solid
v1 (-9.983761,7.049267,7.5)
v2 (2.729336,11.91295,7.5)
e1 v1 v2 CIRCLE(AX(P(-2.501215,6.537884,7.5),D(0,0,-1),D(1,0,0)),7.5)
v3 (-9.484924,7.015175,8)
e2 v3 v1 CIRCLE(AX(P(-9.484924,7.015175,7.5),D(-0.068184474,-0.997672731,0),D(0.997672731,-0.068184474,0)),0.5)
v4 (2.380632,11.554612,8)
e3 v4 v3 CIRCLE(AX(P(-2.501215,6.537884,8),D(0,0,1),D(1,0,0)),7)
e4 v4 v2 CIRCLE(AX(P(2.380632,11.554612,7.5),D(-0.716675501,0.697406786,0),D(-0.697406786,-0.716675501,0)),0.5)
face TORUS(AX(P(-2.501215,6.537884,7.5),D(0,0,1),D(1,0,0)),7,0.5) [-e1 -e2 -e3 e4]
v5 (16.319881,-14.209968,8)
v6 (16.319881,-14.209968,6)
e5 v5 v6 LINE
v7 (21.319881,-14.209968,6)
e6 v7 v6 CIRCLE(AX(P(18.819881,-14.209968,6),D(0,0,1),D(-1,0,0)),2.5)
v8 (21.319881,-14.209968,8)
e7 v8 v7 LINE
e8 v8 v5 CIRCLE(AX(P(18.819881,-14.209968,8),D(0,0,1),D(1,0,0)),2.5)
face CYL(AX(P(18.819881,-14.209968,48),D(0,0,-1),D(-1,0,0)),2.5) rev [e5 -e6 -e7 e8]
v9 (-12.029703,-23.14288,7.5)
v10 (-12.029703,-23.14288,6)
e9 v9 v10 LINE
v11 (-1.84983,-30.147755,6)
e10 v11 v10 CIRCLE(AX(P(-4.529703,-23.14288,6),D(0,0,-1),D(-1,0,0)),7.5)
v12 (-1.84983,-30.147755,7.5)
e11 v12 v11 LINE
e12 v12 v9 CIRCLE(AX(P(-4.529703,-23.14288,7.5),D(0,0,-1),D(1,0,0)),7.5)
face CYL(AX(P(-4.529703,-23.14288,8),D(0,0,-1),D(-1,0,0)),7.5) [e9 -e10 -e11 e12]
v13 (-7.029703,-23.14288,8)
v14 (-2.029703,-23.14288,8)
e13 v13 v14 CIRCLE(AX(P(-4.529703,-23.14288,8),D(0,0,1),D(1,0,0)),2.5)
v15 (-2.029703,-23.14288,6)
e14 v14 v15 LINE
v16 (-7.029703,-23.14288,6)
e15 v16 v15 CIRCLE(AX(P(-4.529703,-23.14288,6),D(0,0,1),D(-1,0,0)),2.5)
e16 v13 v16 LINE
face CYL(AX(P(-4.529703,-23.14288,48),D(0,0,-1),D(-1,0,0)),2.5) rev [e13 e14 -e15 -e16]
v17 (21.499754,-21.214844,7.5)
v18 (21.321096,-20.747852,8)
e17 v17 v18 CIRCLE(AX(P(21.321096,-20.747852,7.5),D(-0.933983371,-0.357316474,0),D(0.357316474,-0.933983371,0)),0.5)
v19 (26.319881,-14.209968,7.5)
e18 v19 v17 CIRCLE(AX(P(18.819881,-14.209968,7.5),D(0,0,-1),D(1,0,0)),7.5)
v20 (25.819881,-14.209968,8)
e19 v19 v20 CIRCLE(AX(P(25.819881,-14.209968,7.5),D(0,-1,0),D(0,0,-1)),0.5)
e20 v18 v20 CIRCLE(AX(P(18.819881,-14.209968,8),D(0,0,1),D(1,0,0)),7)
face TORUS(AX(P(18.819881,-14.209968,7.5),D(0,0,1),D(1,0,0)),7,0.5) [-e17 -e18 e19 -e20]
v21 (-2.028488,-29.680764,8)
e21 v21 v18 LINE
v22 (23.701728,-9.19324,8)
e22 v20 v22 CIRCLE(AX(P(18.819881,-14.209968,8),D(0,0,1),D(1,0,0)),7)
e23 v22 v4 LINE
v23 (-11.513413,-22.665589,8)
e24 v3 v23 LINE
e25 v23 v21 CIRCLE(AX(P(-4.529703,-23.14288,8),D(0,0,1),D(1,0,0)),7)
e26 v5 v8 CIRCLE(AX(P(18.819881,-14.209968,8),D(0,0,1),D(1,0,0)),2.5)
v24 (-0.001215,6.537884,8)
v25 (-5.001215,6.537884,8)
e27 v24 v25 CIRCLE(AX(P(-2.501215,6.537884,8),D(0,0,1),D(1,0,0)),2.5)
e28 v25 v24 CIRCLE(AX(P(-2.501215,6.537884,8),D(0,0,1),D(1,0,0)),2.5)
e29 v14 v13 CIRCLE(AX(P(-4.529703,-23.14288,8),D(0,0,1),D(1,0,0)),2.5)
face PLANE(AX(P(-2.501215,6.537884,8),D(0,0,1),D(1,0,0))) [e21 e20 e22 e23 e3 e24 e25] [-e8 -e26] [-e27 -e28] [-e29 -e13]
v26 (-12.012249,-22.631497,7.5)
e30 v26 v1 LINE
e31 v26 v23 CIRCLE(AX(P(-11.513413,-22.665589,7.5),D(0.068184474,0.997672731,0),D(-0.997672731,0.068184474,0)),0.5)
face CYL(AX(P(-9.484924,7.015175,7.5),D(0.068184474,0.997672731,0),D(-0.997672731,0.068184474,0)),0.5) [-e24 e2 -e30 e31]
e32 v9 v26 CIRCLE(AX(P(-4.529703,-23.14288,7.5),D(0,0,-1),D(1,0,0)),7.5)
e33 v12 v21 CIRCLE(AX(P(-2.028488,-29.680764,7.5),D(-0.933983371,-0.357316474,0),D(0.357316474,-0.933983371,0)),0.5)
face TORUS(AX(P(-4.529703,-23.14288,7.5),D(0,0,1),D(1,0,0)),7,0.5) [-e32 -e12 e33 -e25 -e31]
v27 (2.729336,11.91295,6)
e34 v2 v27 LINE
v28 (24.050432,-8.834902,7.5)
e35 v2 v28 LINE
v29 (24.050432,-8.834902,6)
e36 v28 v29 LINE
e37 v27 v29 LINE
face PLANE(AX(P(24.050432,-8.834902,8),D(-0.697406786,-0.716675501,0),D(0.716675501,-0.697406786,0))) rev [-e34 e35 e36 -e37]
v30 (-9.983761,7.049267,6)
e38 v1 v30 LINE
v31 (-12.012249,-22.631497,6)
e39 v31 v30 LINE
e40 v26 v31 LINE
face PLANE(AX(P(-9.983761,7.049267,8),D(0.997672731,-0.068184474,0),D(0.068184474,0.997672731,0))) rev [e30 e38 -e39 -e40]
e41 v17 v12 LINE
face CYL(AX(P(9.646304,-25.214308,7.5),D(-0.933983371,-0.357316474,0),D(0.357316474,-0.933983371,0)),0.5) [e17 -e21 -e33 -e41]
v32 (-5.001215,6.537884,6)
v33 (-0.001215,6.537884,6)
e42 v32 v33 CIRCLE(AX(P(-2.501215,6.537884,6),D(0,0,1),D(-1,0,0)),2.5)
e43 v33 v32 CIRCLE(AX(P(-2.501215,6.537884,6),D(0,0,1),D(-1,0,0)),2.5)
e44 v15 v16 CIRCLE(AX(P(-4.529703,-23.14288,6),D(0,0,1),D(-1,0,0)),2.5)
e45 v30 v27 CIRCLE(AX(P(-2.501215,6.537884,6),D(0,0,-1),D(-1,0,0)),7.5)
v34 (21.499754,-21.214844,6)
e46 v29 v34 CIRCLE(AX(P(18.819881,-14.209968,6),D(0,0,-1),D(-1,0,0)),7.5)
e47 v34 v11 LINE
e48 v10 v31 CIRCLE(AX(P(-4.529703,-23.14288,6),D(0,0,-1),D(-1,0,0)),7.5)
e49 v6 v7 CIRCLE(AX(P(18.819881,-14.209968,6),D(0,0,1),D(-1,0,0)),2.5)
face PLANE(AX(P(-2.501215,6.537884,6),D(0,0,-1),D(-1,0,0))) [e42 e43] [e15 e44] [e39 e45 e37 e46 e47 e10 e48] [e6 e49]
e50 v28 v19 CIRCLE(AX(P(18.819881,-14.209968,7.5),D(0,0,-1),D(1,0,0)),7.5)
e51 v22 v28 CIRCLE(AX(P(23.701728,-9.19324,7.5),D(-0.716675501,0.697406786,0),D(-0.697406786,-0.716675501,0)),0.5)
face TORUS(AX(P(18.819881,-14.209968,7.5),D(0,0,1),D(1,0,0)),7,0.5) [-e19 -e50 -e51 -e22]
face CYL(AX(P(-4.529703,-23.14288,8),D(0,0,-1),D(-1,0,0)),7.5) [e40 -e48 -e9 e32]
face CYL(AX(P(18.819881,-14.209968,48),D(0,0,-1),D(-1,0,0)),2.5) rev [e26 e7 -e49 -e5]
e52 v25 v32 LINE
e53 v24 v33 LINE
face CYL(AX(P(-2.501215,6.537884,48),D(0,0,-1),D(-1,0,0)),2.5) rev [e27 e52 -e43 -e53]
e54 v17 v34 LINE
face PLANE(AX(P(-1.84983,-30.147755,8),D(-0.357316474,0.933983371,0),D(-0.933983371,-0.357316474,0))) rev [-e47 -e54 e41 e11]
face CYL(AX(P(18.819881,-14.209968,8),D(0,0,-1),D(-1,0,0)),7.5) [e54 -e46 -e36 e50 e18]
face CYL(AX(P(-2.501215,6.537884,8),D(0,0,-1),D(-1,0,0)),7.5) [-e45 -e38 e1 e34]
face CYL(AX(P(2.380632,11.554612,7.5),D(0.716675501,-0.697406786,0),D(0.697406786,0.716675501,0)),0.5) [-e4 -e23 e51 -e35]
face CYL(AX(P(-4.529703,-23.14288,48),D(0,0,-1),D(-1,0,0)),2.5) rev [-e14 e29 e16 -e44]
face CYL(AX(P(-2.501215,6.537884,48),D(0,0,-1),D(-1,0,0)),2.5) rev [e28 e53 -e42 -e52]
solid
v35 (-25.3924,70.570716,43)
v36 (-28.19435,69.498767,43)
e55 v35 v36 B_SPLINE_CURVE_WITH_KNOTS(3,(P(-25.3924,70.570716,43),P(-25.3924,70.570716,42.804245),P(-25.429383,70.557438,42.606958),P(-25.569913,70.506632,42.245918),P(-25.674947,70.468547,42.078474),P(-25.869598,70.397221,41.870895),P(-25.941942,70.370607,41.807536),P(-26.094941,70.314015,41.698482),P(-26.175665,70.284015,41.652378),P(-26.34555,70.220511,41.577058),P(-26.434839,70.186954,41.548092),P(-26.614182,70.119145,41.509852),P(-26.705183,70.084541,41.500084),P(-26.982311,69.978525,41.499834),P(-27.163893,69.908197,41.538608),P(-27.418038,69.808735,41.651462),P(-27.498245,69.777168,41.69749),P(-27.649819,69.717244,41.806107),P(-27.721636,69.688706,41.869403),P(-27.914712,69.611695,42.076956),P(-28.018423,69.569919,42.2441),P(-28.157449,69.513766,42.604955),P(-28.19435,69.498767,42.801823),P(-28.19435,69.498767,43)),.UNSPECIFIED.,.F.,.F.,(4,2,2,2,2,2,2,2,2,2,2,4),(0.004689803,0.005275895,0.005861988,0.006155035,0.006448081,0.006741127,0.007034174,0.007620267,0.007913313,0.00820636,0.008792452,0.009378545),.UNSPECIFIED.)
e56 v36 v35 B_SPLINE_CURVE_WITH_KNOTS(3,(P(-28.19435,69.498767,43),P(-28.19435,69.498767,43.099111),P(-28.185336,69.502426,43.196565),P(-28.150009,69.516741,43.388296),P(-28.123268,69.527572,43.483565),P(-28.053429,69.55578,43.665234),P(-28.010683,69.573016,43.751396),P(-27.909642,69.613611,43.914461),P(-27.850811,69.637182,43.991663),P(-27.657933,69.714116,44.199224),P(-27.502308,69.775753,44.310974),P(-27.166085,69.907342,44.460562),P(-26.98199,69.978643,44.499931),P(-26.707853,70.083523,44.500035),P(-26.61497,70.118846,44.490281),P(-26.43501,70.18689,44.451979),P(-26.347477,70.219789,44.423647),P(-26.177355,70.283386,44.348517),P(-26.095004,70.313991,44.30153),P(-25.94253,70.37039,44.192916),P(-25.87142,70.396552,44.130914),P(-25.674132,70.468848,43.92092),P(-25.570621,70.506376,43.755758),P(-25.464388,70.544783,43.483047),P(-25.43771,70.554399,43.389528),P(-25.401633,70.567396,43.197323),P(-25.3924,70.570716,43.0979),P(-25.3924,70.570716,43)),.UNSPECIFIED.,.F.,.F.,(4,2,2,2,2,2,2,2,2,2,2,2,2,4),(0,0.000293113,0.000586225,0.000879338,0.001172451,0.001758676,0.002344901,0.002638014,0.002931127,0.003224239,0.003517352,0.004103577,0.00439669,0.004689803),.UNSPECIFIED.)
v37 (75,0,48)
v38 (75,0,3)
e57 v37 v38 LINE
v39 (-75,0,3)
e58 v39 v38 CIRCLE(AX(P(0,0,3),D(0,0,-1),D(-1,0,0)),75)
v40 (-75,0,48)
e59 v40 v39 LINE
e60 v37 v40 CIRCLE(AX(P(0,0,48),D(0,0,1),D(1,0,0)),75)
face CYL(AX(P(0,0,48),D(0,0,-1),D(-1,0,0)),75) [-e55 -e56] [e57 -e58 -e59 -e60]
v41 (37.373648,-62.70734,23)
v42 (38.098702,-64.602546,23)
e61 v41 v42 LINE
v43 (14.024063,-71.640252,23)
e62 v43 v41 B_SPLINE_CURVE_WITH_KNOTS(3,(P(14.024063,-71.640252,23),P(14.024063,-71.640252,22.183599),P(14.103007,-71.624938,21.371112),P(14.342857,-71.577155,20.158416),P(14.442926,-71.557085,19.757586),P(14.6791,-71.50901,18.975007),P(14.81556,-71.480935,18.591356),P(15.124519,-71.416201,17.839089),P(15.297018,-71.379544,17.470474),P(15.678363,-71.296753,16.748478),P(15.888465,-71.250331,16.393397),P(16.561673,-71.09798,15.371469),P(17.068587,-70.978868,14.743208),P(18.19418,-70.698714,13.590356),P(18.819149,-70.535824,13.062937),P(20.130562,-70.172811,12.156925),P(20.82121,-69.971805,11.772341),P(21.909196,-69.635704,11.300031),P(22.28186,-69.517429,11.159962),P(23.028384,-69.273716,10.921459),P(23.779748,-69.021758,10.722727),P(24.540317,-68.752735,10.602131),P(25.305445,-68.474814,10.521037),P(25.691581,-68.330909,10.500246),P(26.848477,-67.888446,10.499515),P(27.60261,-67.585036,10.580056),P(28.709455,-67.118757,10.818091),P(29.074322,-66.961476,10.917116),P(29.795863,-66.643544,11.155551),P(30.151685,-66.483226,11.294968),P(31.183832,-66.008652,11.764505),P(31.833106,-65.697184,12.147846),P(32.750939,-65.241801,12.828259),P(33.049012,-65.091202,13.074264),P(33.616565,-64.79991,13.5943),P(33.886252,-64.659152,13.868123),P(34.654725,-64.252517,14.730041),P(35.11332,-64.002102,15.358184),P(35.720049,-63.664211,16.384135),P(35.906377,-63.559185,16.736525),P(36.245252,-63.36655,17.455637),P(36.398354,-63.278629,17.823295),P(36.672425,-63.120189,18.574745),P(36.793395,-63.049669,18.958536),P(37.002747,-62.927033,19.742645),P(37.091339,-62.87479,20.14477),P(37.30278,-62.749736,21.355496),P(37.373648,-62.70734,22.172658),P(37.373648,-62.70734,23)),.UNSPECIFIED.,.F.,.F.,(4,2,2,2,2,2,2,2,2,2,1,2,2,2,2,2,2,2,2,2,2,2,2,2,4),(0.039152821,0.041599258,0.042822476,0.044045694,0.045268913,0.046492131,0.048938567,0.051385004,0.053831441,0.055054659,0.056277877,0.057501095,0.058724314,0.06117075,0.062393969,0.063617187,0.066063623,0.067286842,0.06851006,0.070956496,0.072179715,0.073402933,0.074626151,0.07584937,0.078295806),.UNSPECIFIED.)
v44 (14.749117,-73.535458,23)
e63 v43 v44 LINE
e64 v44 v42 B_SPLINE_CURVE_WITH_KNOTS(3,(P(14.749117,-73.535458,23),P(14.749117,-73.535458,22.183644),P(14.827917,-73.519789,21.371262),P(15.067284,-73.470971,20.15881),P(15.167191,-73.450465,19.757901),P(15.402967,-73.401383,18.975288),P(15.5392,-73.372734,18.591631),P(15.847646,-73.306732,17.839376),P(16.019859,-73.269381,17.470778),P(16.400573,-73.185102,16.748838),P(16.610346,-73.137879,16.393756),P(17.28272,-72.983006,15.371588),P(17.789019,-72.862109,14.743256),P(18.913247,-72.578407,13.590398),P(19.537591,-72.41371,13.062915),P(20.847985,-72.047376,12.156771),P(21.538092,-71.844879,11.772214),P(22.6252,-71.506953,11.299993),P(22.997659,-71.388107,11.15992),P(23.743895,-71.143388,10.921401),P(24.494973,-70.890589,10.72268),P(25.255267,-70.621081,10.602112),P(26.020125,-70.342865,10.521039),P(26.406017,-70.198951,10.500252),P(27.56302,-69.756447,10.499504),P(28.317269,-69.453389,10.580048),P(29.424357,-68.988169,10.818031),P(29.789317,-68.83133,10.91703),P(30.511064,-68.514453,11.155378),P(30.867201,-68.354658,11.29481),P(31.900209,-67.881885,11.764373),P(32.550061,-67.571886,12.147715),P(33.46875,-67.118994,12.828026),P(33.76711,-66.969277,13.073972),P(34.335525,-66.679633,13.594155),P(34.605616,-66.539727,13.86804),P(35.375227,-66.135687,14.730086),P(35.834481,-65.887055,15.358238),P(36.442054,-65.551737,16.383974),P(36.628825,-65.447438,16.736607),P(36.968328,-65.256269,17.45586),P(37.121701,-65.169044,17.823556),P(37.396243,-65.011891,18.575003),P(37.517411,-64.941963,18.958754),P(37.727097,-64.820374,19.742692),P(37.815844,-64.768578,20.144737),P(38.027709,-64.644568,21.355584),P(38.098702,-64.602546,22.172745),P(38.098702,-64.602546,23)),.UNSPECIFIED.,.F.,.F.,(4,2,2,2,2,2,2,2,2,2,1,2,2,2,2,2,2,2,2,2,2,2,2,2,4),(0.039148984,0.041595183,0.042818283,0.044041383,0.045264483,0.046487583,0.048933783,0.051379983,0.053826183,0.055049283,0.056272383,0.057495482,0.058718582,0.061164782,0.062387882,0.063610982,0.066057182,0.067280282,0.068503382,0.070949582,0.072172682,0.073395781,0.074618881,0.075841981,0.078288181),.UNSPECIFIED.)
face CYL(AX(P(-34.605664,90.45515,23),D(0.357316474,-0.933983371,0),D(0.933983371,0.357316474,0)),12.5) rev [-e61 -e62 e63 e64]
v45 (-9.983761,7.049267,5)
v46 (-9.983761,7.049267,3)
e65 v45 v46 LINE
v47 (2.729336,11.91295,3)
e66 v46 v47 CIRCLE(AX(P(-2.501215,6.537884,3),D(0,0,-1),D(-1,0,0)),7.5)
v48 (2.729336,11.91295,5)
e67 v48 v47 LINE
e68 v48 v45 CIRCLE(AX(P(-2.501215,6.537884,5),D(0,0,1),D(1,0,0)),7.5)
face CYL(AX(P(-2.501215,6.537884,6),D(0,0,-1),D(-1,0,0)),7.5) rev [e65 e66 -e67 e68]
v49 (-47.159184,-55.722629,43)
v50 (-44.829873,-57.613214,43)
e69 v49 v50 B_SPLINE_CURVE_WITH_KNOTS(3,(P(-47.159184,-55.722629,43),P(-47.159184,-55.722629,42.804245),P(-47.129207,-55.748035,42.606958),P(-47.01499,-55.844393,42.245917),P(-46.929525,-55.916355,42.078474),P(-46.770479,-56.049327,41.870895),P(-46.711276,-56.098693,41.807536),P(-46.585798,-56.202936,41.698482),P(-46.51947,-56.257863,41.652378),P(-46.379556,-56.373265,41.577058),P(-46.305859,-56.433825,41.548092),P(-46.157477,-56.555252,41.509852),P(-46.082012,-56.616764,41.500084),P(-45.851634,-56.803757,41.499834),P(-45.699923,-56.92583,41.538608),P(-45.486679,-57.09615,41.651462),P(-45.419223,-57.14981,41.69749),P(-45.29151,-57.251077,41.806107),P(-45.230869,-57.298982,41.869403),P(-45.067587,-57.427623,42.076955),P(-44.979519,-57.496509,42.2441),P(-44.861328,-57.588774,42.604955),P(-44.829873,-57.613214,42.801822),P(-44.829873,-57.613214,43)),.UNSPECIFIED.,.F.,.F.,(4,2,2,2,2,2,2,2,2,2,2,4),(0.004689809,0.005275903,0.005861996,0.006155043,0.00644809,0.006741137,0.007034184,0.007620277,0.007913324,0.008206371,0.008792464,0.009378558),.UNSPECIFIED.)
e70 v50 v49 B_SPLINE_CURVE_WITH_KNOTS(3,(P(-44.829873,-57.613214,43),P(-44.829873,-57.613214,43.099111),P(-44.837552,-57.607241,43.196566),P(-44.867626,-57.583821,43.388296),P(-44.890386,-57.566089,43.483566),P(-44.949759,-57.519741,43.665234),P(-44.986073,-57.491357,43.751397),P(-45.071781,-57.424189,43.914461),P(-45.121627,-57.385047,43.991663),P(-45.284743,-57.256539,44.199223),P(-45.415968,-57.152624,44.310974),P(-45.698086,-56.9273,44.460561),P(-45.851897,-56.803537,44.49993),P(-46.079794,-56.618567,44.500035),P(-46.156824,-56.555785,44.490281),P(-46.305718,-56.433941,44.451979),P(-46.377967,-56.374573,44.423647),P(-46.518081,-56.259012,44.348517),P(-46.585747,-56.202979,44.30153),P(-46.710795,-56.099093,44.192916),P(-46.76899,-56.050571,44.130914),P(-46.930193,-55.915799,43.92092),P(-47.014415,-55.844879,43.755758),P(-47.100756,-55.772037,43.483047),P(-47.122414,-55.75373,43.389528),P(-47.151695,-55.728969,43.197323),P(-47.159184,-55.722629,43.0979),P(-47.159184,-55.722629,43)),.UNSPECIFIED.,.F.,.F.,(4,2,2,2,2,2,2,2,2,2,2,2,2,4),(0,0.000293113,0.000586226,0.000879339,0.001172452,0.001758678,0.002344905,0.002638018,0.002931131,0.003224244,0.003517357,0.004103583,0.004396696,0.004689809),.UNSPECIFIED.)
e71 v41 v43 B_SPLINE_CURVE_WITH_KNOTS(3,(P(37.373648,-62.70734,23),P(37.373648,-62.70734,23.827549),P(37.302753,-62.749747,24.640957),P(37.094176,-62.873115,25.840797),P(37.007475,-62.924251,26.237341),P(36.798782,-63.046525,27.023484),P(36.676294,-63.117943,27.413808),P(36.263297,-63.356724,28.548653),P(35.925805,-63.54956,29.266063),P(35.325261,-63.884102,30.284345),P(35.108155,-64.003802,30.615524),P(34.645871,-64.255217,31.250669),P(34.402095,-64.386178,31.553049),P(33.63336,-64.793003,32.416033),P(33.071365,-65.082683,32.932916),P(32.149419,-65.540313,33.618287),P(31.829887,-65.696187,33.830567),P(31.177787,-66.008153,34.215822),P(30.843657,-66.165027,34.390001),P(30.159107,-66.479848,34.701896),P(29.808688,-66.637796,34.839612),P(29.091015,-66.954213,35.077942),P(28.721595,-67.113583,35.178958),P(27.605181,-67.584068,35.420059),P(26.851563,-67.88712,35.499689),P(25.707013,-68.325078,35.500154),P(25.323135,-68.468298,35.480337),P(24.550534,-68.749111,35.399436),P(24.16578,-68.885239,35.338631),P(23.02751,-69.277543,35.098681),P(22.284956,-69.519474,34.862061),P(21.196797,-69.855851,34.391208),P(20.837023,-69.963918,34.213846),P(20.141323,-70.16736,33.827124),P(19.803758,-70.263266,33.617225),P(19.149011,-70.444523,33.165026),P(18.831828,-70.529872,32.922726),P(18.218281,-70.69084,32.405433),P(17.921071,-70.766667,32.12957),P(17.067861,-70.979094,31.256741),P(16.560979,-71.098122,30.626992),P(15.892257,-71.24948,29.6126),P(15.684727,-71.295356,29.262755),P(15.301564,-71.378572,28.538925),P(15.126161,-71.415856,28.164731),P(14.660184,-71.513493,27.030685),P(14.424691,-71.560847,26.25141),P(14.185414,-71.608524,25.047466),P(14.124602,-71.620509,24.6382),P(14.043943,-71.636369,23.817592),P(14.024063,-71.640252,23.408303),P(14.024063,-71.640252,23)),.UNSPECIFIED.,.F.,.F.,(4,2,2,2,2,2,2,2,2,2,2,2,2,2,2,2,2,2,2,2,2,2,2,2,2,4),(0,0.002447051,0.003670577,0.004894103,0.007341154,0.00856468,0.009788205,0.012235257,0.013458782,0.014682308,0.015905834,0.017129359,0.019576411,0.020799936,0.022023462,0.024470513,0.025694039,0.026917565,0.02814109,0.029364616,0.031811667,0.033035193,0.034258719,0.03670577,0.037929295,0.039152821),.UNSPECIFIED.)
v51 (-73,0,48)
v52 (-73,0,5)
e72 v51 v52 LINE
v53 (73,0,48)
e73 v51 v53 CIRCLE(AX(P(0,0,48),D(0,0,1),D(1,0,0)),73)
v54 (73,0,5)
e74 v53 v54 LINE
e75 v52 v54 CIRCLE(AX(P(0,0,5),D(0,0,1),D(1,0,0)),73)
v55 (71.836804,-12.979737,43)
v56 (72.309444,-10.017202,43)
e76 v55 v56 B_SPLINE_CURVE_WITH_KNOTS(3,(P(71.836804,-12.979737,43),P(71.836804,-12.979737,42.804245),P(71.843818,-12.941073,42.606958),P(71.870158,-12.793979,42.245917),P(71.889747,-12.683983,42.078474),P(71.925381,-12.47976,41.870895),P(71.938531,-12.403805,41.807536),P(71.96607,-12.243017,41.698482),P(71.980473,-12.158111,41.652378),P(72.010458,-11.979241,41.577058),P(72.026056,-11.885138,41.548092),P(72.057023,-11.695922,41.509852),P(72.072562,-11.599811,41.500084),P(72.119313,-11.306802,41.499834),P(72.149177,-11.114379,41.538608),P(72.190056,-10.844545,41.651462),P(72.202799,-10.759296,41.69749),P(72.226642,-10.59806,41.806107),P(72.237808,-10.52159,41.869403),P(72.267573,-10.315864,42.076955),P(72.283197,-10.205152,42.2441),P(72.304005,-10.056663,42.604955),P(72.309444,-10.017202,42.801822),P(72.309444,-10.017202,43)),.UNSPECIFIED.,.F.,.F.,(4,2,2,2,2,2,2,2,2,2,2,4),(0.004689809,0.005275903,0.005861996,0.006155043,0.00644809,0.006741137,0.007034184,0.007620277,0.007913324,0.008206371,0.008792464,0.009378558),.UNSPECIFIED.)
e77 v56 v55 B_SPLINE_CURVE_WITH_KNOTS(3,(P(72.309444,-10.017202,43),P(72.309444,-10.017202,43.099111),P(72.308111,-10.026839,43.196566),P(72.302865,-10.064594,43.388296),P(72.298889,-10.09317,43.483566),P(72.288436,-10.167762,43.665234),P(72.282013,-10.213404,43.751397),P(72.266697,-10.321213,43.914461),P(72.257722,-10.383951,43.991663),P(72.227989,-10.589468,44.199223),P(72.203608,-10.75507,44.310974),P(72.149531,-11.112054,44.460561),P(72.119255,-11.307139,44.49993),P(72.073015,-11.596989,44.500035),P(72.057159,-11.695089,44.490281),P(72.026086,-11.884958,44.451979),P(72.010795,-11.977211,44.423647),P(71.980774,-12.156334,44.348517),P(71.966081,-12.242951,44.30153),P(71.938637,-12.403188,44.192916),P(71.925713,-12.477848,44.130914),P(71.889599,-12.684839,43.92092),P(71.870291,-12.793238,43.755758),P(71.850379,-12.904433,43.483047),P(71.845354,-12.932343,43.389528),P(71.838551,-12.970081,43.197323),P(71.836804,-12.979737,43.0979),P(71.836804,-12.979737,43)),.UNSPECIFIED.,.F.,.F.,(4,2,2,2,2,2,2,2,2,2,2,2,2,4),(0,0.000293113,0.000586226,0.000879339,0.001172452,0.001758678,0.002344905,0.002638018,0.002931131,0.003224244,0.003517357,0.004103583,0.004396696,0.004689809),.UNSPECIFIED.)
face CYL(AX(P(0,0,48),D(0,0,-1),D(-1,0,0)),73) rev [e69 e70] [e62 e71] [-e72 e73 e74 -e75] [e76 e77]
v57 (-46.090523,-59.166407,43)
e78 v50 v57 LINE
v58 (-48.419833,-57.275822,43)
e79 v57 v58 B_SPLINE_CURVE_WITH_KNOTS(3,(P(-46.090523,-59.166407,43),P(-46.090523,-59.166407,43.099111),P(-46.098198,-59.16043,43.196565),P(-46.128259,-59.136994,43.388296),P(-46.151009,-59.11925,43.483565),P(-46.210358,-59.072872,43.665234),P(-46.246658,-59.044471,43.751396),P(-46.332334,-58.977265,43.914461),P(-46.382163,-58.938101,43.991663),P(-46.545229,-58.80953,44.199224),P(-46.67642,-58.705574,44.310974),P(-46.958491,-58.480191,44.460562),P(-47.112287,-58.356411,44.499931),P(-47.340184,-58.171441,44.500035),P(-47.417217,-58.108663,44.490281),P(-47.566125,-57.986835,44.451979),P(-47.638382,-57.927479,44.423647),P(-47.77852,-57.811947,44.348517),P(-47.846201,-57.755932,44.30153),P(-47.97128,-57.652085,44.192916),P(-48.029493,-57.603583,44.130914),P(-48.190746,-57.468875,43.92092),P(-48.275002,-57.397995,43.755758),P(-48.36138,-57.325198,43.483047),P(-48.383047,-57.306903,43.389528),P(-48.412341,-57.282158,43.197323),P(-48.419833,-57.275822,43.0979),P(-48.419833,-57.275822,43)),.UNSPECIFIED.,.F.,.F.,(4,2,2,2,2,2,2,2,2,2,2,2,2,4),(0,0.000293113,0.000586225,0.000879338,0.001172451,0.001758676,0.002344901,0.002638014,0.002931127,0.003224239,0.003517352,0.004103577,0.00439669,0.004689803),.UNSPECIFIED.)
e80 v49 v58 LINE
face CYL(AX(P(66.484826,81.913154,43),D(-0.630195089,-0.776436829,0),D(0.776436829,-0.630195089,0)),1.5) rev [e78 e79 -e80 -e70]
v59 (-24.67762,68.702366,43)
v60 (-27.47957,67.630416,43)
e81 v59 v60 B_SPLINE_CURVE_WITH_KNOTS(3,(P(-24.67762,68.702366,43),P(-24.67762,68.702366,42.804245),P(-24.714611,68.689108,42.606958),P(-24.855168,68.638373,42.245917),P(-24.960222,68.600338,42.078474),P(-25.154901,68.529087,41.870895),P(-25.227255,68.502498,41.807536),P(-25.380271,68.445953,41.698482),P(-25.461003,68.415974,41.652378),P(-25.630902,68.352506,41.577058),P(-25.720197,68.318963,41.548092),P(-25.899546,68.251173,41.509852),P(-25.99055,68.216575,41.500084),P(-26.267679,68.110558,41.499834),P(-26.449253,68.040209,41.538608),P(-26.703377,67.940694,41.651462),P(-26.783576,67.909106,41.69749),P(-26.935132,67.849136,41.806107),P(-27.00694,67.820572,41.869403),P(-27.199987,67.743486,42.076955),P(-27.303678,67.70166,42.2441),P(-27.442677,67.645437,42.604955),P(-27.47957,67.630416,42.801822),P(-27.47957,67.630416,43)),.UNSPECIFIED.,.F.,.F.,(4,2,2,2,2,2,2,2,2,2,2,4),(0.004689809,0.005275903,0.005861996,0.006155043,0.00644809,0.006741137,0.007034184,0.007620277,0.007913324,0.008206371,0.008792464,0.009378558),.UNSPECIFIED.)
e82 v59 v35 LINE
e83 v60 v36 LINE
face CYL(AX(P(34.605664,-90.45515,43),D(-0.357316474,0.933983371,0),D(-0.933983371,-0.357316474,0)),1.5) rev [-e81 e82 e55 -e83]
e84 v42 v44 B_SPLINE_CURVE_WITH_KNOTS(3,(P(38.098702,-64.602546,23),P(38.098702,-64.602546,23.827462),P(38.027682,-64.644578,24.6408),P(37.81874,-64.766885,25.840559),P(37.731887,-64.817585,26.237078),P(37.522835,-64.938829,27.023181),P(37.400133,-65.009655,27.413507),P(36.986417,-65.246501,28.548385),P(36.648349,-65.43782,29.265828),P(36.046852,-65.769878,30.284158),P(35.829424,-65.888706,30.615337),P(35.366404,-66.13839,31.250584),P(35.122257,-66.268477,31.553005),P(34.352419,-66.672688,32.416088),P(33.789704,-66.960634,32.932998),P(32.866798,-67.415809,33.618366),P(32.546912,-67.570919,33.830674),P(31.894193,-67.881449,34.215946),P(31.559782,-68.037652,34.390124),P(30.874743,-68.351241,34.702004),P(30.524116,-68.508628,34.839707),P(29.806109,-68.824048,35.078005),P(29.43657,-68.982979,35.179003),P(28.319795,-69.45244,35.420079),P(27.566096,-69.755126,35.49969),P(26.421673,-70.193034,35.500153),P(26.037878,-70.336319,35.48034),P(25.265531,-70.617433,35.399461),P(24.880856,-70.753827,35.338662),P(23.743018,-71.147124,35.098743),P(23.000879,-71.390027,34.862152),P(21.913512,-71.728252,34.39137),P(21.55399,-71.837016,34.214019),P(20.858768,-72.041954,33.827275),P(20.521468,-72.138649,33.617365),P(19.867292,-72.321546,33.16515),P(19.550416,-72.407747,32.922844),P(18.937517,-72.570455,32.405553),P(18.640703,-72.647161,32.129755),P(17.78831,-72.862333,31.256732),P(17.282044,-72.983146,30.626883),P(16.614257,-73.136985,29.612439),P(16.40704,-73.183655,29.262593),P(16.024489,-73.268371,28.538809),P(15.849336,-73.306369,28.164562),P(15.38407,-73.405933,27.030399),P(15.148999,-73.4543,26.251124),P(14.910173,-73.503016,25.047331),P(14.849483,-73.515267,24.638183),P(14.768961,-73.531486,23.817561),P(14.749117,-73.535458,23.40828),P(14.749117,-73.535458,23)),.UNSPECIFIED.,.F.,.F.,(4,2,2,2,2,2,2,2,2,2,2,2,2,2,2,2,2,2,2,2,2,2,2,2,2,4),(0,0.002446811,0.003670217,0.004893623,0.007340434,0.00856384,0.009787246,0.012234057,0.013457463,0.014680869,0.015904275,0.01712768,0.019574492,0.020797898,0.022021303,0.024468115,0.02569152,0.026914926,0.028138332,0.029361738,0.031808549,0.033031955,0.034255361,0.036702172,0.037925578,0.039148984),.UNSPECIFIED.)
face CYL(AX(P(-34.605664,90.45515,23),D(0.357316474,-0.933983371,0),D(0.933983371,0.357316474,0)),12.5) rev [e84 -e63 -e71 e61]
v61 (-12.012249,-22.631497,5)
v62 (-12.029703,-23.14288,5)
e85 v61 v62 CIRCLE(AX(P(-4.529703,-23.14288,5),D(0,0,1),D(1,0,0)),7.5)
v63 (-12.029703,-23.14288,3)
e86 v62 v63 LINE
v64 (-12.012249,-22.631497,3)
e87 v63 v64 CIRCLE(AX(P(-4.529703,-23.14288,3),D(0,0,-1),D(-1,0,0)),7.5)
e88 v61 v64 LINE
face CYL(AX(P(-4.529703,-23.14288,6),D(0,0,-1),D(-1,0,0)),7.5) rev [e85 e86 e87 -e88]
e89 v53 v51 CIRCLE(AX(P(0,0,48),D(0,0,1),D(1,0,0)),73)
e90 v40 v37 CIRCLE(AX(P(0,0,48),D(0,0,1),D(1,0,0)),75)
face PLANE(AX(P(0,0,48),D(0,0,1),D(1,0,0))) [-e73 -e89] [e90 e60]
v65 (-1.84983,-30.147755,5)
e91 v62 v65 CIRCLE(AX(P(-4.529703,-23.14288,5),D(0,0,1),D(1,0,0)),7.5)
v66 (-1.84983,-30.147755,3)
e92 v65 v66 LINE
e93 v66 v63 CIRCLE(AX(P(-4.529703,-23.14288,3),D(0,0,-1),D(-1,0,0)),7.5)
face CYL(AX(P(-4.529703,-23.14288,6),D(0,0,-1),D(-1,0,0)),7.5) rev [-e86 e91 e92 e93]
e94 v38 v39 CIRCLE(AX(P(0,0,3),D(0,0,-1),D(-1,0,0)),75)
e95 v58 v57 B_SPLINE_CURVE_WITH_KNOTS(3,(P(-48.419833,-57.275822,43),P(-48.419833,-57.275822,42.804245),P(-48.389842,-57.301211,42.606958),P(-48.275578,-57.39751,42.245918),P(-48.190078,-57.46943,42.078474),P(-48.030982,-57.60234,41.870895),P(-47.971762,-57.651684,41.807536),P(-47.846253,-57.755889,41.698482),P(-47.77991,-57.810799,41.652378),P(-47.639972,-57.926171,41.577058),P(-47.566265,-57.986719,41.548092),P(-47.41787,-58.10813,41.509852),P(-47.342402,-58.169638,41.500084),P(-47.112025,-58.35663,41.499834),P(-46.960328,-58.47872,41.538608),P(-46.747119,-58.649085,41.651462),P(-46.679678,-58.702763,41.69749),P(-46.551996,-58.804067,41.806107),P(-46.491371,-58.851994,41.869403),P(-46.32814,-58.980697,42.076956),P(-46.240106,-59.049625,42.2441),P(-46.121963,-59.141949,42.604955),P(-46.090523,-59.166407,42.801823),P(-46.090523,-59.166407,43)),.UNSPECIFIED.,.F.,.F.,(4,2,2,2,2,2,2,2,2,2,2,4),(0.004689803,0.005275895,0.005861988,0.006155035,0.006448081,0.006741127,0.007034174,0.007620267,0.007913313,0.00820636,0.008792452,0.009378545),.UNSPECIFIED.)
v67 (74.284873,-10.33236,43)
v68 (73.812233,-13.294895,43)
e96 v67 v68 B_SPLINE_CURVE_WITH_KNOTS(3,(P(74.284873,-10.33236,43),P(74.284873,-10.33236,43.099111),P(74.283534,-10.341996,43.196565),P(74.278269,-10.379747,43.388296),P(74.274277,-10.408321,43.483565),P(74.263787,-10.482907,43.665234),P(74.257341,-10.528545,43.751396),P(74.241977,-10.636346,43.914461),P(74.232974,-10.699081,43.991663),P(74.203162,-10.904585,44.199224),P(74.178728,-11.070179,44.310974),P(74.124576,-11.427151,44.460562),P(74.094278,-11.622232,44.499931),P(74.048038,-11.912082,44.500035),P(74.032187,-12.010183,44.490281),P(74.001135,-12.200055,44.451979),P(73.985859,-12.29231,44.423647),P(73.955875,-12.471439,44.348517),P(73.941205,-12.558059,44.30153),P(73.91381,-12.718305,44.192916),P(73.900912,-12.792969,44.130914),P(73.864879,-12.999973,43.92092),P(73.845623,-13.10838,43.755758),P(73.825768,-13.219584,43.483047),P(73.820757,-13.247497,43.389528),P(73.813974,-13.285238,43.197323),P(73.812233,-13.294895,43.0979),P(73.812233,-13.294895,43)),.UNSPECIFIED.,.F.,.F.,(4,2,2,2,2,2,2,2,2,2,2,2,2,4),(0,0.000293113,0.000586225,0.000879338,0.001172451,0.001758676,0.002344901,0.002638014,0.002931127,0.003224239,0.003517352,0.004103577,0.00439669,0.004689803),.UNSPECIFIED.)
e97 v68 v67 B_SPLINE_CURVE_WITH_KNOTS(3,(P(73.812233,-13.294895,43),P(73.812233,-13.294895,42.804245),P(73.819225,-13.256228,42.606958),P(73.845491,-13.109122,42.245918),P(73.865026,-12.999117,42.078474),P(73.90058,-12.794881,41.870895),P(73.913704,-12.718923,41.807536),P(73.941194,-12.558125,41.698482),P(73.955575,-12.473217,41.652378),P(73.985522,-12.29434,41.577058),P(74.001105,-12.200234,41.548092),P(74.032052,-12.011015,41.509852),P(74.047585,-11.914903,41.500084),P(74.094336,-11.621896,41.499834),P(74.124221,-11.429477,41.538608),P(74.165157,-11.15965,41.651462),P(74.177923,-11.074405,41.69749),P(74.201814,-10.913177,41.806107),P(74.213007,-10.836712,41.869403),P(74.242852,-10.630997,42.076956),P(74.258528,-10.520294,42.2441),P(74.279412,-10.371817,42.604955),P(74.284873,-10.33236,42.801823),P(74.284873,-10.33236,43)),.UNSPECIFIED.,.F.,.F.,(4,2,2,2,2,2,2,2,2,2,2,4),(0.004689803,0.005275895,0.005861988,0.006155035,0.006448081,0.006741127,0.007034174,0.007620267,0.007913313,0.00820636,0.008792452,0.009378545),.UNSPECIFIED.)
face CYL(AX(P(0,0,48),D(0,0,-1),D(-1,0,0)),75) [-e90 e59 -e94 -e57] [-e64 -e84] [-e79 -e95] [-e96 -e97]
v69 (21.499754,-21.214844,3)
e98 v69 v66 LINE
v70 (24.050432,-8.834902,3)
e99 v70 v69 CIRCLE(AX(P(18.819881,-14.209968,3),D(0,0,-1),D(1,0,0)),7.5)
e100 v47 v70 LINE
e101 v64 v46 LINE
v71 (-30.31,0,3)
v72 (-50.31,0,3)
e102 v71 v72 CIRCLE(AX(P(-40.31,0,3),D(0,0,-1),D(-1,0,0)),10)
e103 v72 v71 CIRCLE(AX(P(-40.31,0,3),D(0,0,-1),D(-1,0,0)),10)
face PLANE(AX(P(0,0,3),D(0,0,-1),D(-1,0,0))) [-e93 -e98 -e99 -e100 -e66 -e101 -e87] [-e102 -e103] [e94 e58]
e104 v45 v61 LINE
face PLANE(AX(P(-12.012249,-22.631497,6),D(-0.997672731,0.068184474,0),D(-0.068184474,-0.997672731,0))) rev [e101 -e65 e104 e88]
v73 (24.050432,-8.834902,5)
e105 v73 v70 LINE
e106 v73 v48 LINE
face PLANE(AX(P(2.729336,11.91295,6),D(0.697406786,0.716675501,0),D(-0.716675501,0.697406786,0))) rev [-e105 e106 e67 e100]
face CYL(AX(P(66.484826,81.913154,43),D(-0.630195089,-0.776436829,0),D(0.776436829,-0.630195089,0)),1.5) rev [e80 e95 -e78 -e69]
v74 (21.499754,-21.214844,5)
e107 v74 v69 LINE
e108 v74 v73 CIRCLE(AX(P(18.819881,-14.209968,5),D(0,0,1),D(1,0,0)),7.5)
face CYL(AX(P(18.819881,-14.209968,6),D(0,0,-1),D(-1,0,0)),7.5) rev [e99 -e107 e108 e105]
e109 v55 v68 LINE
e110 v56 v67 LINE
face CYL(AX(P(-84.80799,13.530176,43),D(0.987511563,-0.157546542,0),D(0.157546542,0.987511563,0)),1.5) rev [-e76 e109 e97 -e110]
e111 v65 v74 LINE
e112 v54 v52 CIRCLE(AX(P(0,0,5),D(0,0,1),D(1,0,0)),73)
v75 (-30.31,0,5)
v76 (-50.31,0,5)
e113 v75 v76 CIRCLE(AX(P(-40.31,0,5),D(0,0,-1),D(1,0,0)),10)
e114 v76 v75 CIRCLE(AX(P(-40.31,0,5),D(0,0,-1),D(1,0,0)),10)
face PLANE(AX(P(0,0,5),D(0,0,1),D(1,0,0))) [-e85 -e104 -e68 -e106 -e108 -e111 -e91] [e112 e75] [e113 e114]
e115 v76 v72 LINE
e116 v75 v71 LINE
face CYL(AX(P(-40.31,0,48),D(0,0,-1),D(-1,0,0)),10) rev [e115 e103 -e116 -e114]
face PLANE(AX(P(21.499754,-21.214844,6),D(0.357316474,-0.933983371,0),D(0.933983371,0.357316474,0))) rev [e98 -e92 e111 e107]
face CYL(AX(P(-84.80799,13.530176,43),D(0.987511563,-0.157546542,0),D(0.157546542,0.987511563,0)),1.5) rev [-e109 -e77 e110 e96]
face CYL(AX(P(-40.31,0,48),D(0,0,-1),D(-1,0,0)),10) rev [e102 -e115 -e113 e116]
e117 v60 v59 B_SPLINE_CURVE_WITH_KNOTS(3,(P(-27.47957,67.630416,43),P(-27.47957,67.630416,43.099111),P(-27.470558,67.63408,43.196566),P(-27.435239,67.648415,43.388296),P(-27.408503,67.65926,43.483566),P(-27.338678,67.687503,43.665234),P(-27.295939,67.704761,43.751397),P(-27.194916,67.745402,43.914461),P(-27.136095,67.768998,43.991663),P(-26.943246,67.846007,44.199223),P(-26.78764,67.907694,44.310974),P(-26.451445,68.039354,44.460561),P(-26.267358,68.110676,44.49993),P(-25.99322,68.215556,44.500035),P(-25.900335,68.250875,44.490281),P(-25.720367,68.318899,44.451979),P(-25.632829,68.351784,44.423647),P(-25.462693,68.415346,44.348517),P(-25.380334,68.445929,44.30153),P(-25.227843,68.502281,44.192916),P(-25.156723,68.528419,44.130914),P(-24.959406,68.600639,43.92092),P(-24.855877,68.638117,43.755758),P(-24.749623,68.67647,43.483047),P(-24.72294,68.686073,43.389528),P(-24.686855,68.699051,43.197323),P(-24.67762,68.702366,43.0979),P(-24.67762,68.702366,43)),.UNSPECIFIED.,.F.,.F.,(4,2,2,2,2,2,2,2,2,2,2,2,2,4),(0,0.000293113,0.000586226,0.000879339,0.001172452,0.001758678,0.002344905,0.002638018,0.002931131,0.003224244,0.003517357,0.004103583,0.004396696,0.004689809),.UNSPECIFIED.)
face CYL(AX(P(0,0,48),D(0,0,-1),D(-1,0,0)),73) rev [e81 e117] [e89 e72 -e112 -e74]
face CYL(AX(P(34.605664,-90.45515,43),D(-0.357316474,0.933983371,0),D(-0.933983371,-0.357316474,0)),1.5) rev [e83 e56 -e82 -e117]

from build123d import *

# Parameters (mm, degrees)
SKETCH_1_R                = 75
SKETCH_1_R_2              = 73
BOSS_EXTRUDE_1_DEPTH      = 48
SKETCH_2_R                = 75
BOSS_EXTRUDE_2_DEPTH      = 5
SKETCH_4_R                = 10
CUT_EXTRUDE_8_DEPTH       = 117.421647472
SKETCH_8_R                = 75
CUT_EXTRUDE_10_DEPTH      = 3
CUT_EXTRUDE_12_REACH      = 185.592
CUT_EXTRUDE_12_END_RADIUS = 73
SKETCH_11_R               = 12.5
SKETCH_20_R               = 2.5
CUT_EXTRUDE_19_DEPTH      = 117.421647642
SKETCH_21_R               = 2.5
BOSS_EXTRUDE_3_DEPTH      = 3
CUT_EXTRUDE_21_DEPTH      = 6
FILLET_2_R                = 0.5
CUT_EXTRUDE_22_REACH      = 185.592
CUT_EXTRUDE_22_END_RADIUS = 73
SKETCH_24_R               = 1.5
CIRCULAR_PATTERN_1_COUNT  = 3


with BuildPart() as part:
    # Sketch 1 → Boss-Extrude 1 (new body)
    with BuildSketch(Plane.XY):
        Circle(SKETCH_1_R)
        Circle(SKETCH_1_R_2, mode=Mode.SUBTRACT)
    extrude(amount=BOSS_EXTRUDE_1_DEPTH)

    # Sketch 2 → Boss-Extrude 2 (add)
    with BuildSketch(Plane.XY):
        Circle(SKETCH_2_R)
    extrude(amount=BOSS_EXTRUDE_2_DEPTH)

    # Sketch 4 → Cut-Extrude 8 (cut, through all)
    with BuildSketch(Plane.XY):
        with Locations((-40.31, 0)):
            Circle(SKETCH_4_R)
    extrude(amount=CUT_EXTRUDE_8_DEPTH, mode=Mode.SUBTRACT)

    # Sketch 8 → Cut-Extrude 10 (cut)
    with BuildSketch(Plane(origin=(0, 0, 0), x_dir=(-1, 0, 0), z_dir=(0, 0, -1))):
        Circle(SKETCH_8_R)
        with BuildLine():
            Line((12.012248906, -22.631496582), (9.983760796, 7.049267155))
            ThreePointArc((9.983760796, 7.049267155), (5.18108887, 13.542758882), (-2.729335581, 11.912949859))
            Line((-2.729335581, 11.912949859), (-24.05043175, -8.834902033))
            ThreePointArc((-24.05043175, -8.834902033), (-26.165589934, -15.723427277), (-21.499754406, -21.214843578))
            Line((-21.499754406, -21.214843578), (1.849829873, -30.147755422))
            ThreePointArc((1.849829873, -30.147755422), (8.989518573, -29.172809562), (12.012248906, -22.631496582))
        make_face(mode=Mode.SUBTRACT)
    extrude(amount=-CUT_EXTRUDE_10_DEPTH, mode=Mode.SUBTRACT)

    # Cut-Extrude 12: up to this cylinder (the profile starts outside it)
    cut_extrude_12_end = Plane(origin=(0, 0, 23), z_dir=(0, 0, -1)) * Cylinder(CUT_EXTRUDE_12_END_RADIUS, 518.184, mode=Mode.PRIVATE)
    # Sketch 11 → Cut-Extrude 12 (cut, up to the surface)
    with BuildSketch(Plane(origin=(26.798735532, -70.048752836, 0), x_dir=(-0.9339833711458582, -0.35731647376383047, 0), z_dir=(0.35731647376383047, -0.9339833711458583, 0)), mode=Mode.PRIVATE) as cut_extrude_12_sk1:
        with Locations(Location((0, -23, 0), (0, 0, 180))):
            Circle(SKETCH_11_R)
    cut_extrude_12_tool1 = extrude(cut_extrude_12_sk1.sketch, amount=-CUT_EXTRUDE_12_REACH, mode=Mode.PRIVATE) - cut_extrude_12_end
    add(cut_extrude_12_tool1.solids().sort_by_distance((26.798736, -70.048753, 23))[0], mode=Mode.SUBTRACT)

    # Sketch 20 → Cut-Extrude 19 (cut, through all)
    with BuildSketch(Plane(origin=(0, 0, 0), x_dir=(-1, 0, 0), z_dir=(0, 0, -1))):
        with Locations((2.501215316, 6.537883598)):
            Circle(SKETCH_20_R)
        with Locations((4.529703426, -23.142880139)):
            Circle(SKETCH_20_R)
        with Locations((-18.819880853, -14.209968294)):
            Circle(SKETCH_20_R)
    extrude(amount=-CUT_EXTRUDE_19_DEPTH, mode=Mode.SUBTRACT)

    # Sketch 21 → Boss-Extrude 3 (add)
    with BuildSketch(Plane.XY.offset(5)):
        with BuildLine():
            Line((24.05043175, -8.834902033), (2.729335581, 11.912949859))
            ThreePointArc((2.729335581, 11.912949859), (-5.18108887, 13.542758882), (-9.983760796, 7.049267155))
            Line((-9.983760796, 7.049267155), (-12.012248906, -22.631496582))
            ThreePointArc((-12.012248906, -22.631496582), (-8.989518573, -29.172809562), (-1.849829873, -30.147755422))
            Line((-1.849829873, -30.147755422), (21.499754406, -21.214843578))
            ThreePointArc((21.499754406, -21.214843578), (26.165589934, -15.723427277), (24.05043175, -8.834902033))
        make_face()
        with Locations(Location((-4.529703426, -23.142880139, 0), (0, 0, 180))):
            Circle(SKETCH_21_R, mode=Mode.SUBTRACT)
        with Locations(Location((18.819880853, -14.209968294, 0), (0, 0, 180))):
            Circle(SKETCH_21_R, mode=Mode.SUBTRACT)
        with Locations(Location((-2.501215316, 6.537883598, 0), (0, 0, 180))):
            Circle(SKETCH_21_R, mode=Mode.SUBTRACT)
    extrude(amount=BOSS_EXTRUDE_3_DEPTH)

    # Sketch 22 → Cut-Extrude 21 (cut)
    with BuildSketch(Plane(origin=(0, 0, 0), x_dir=(-1, 0, 0), z_dir=(0, 0, -1))):
        with BuildLine():
            Line((-2.729335581, 11.912949859), (-24.05043175, -8.834902033))
            ThreePointArc((-24.05043175, -8.834902033), (-26.165589934, -15.723427277), (-21.499754406, -21.214843578))
            Line((-21.499754406, -21.214843578), (1.849829873, -30.147755422))
            ThreePointArc((1.849829873, -30.147755422), (8.989518573, -29.172809562), (12.012248906, -22.631496582))
            Line((12.012248906, -22.631496582), (9.983760796, 7.049267155))
            ThreePointArc((9.983760796, 7.049267155), (5.18108887, 13.542758882), (-2.729335581, 11.912949859))
        make_face()
    extrude(amount=-CUT_EXTRUDE_21_DEPTH, mode=Mode.SUBTRACT)


with BuildPart() as cut_extrude_21_piece_1:
    # of the separate pieces the step leaves, piece 1, a body of its own (cut_extrude_21_pieces)
    add(part.part.solids().sort_by_distance((75, 0, 48))[0])

    # Cut-Extrude 22: up to this cylinder (the profile starts outside it)
    cut_extrude_22_end = Plane(origin=(0, 0, 43), z_dir=(0, 0, -1)) * Cylinder(CUT_EXTRUDE_22_END_RADIUS, 518.184, mode=Mode.PRIVATE)
    # Sketch 24 → Cut-Extrude 22 (cut, up to the surface)
    with BuildSketch(Plane(origin=(-26.798735532, 70.048752836, 0), x_dir=(0.9339833711458588, 0.3573164737638288, 0), z_dir=(-0.3573164737638288, 0.9339833711458588, 0)), mode=Mode.PRIVATE) as cut_extrude_22_sk1:
        with Locations(Location((0, -43, 0), (0, 0, 180))):
            Circle(SKETCH_24_R)
    cut_extrude_22_tool1 = extrude(cut_extrude_22_sk1.sketch, amount=-CUT_EXTRUDE_22_REACH, mode=Mode.PRIVATE) - cut_extrude_22_end
    cut_extrude_22 = cut_extrude_22_tool1.solids().sort_by_distance((-26.798736, 70.048753, 43))[0]
    add(cut_extrude_22, mode=Mode.SUBTRACT)

    # Circular pattern 1: Cut-Extrude 22 ×3 about axis
    circular_pattern_1_axis = Axis((0, 0, 0), (0, 0, 1))
    for i in range(1, CIRCULAR_PATTERN_1_COUNT):
        add(cut_extrude_22.rotate(circular_pattern_1_axis, i * 360 / CIRCULAR_PATTERN_1_COUNT), mode=Mode.SUBTRACT)


with BuildPart() as cut_extrude_21_piece_2:
    # of the separate pieces the step leaves, piece 2, a body of its own (cut_extrude_21_pieces)
    add(part.part.solids().sort_by_distance((-1.849829873, -30.147755422, 6))[0])

    # Fillet 2
    fillet_2_edges = [cut_extrude_21_piece_2.edges().sort_by_distance(p)[0] for p in [
        (13.389883665, 1.539023913, 8),
        (-5.18108887, 13.542758882, 8),
        (-10.998004851, -7.791114713, 8),
        (-8.989518573, -29.172809562, 8),
        (9.824962267, -25.6812995, 8),
        (26.165589934, -15.723427277, 8),
    ]]
    fillet(fillet_2_edges, radius=FILLET_2_R)


solid = Compound([cut_extrude_21_piece_1.part, cut_extrude_21_piece_2.part])
